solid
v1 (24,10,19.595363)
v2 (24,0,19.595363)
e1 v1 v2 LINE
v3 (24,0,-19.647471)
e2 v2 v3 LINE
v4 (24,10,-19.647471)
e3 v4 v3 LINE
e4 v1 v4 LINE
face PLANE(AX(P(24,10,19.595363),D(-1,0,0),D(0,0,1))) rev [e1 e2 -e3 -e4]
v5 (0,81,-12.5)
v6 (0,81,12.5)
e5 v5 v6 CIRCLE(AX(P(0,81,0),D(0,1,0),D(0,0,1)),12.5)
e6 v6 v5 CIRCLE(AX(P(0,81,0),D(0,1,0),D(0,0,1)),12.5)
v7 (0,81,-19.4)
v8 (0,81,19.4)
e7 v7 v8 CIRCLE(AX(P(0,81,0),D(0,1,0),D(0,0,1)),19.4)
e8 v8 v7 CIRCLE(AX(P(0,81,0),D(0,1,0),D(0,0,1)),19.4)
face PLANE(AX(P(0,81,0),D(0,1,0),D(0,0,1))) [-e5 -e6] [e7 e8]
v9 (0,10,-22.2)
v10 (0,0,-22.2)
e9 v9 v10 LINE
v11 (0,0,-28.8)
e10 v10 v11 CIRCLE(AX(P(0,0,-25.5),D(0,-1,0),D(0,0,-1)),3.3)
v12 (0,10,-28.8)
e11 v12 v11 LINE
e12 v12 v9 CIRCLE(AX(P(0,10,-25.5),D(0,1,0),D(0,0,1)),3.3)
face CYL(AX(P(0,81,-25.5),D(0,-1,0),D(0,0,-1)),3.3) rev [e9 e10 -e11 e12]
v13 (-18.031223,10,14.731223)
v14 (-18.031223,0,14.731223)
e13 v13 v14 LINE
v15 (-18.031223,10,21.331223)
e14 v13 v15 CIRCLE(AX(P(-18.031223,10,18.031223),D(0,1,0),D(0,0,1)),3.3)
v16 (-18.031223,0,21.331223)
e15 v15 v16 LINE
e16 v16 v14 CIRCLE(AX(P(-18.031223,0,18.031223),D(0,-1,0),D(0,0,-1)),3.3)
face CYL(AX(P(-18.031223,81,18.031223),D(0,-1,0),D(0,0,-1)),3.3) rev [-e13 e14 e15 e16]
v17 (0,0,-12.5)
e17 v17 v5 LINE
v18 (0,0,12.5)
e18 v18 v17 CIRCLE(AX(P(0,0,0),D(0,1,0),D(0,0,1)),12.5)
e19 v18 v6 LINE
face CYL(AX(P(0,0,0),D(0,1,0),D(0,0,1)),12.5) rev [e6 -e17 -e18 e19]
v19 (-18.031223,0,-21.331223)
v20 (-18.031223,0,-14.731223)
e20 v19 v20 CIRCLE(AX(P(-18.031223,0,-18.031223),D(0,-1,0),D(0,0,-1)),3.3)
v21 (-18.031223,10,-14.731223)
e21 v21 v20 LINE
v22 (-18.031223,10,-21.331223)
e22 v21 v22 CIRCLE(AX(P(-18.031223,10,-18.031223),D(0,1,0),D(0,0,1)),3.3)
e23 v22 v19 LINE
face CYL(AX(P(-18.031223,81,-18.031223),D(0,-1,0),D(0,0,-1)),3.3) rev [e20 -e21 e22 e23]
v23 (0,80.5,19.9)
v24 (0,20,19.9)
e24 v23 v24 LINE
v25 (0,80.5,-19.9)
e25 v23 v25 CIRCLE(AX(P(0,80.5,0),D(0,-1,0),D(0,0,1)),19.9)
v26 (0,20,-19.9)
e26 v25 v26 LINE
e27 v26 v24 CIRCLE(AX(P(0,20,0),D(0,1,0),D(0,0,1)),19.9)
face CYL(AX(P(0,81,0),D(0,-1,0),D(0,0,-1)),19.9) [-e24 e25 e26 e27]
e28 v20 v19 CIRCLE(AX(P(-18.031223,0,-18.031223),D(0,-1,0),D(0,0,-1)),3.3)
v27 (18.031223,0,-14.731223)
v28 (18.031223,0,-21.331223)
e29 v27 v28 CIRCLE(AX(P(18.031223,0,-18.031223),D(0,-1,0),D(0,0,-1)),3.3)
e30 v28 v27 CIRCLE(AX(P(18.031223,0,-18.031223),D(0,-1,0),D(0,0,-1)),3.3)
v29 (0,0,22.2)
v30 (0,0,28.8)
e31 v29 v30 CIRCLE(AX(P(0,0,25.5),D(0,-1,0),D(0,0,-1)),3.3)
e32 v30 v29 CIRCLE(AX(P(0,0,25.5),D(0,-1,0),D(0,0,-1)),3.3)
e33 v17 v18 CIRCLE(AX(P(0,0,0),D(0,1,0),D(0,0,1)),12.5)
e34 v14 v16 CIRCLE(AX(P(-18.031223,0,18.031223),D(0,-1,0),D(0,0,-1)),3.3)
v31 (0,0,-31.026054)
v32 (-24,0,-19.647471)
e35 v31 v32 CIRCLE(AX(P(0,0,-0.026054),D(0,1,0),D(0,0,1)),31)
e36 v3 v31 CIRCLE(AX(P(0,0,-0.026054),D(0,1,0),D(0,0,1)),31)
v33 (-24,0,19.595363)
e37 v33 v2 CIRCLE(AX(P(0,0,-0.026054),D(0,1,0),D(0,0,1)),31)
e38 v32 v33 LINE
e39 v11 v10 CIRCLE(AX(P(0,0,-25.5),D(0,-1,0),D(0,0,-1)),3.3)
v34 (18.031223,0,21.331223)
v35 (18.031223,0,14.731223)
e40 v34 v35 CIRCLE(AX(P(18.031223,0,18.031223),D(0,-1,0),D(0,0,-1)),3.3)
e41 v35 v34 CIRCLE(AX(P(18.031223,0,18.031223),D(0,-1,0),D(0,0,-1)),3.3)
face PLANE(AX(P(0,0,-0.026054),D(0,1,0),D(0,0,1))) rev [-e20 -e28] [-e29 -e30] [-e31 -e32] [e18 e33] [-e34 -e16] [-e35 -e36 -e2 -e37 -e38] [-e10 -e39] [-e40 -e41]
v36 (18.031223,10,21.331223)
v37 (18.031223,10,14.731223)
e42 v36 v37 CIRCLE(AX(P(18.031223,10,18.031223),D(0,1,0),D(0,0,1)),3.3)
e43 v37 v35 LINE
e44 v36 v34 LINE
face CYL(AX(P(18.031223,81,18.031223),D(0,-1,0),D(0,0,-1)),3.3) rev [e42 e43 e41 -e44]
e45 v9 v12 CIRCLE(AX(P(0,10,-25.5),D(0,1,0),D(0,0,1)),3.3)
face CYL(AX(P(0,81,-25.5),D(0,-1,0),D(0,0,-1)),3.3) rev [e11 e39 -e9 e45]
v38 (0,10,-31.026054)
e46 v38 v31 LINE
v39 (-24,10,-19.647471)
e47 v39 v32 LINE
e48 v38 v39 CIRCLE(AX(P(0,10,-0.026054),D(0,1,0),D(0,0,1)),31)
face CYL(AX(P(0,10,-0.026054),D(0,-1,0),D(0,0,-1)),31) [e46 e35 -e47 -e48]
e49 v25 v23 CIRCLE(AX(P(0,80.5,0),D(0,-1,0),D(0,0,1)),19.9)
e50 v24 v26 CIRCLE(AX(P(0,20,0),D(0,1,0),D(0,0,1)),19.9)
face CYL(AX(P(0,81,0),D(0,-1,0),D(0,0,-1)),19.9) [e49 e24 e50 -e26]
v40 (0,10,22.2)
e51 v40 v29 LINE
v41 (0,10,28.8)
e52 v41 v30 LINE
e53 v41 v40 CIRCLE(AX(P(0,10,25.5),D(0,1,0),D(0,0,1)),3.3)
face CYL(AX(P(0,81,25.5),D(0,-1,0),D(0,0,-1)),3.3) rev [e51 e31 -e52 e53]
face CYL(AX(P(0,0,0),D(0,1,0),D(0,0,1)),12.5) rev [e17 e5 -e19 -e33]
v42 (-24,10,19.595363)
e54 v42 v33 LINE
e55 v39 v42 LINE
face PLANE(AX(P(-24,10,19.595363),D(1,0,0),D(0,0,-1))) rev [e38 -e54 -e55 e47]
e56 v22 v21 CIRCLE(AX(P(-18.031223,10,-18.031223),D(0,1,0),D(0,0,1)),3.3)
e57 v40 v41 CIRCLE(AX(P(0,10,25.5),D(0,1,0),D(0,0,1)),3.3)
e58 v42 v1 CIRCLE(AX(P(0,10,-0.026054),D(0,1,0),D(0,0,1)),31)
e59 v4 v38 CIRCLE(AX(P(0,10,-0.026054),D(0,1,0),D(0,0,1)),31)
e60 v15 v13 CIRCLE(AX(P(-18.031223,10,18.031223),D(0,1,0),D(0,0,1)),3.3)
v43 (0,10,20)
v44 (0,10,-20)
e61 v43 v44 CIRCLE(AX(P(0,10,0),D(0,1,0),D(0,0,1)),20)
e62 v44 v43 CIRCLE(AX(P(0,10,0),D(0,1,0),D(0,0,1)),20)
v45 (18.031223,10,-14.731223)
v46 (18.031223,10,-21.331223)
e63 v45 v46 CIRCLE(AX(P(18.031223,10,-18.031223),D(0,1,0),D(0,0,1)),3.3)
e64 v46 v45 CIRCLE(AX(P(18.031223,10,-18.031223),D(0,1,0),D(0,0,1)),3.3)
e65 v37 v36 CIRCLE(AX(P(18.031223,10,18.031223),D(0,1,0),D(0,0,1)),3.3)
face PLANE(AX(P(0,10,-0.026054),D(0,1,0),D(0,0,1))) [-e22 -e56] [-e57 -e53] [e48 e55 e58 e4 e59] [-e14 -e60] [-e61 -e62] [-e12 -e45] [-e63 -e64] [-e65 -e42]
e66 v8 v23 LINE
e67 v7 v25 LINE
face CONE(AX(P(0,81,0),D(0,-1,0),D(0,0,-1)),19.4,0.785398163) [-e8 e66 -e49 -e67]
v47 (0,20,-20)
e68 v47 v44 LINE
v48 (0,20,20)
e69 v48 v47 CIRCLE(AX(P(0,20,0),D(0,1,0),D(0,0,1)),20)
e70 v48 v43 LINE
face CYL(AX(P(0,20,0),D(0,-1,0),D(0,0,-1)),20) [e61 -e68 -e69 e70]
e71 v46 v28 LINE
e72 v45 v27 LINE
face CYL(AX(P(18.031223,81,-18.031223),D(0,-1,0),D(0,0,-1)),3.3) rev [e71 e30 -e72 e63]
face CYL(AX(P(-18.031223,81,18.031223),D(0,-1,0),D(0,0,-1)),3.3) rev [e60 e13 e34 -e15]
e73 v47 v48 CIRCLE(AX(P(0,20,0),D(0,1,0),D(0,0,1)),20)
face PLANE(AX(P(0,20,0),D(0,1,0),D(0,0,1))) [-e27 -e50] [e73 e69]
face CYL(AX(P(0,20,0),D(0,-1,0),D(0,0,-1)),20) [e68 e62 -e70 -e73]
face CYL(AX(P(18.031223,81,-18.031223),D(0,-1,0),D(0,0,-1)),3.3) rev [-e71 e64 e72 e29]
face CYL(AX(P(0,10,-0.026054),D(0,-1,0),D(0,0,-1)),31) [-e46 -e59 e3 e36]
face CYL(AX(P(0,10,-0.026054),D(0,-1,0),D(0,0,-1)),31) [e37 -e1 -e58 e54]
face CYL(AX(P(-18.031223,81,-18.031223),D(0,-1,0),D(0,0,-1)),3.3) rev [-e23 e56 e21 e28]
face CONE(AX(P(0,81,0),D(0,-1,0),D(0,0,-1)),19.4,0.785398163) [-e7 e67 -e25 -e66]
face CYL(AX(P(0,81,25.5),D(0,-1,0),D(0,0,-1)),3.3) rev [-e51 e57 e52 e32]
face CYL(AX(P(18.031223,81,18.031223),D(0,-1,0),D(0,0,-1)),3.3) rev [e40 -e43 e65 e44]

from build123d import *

# Parameters (mm, degrees)
EXTRUDE_1_DEPTH     = 10
SKETCH_2_R          = 20
EXTRUDE_2_DEPTH     = 10
SKETCH_3_R          = 19.9
EXTRUDE_3_DEPTH     = 61
SKETCH_5_R          = 12.5
CUT_EXTRUDE_1_DEPTH = 90.997866916
SKETCH_6_R          = 3.3
CUT_EXTRUDE_2_DEPTH = 90.997866916
CHAMFER_1_SIZE      = 0.5


with BuildPart() as part:
    # 草图1 → 拉伸1 (new body)
    with BuildSketch(Plane(origin=(0, 0, 0), x_dir=(1, 0, 0), z_dir=(0, 1, 0))):
        with BuildLine():
            Line((24, -19.595362506), (24, 19.647471235))
            ThreePointArc((24, 19.647471235), (0, 31.026054364), (-24, 19.647471235))
            Line((-24, 19.647471235), (-24, -19.595362506))
            ThreePointArc((-24, -19.595362506), (0, -30.973945636), (24, -19.595362506))
        make_face()
    extrude(amount=EXTRUDE_1_DEPTH)

    # 草图2 → 拉伸2 (add)
    with BuildSketch(Plane(origin=(0, 10, 0), x_dir=(-1, 0, 0), z_dir=(0, 1, 0))):
        with Locations(Location((0, 0, 0), (0, 0, 90))):
            Circle(SKETCH_2_R)
    extrude(amount=EXTRUDE_2_DEPTH)

    # 草图3 → 拉伸3 (add)
    with BuildSketch(Plane(origin=(0, 20, 0), x_dir=(-1, 0, 0), z_dir=(0, 1, 0))):
        with Locations(Location((0, 0, 0), (0, 0, 270))):
            Circle(SKETCH_3_R)
    extrude(amount=EXTRUDE_3_DEPTH)

    # 草图5 → 切除-拉伸1 (cut, through all)
    with BuildSketch(Plane(origin=(0, 81, 0), x_dir=(-1, 0, 0), z_dir=(0, 1, 0))):
        with Locations(Location((0, 0, 0), (0, 0, 90))):
            Circle(SKETCH_5_R)
    extrude(amount=-CUT_EXTRUDE_1_DEPTH, mode=Mode.SUBTRACT)

    # 草图6 → 切除-拉伸2 (cut, through all)
    with BuildSketch(Plane.XZ):
        with Locations(Location((18.03122292, -18.03122292, 0), (0, 0, 270))):
            Circle(SKETCH_6_R)
        with Locations(Location((0, -25.5, 0), (0, 0, 270))):
            Circle(SKETCH_6_R)
        with Locations(Location((-18.03122292, -18.03122292, 0), (0, 0, 270))):
            Circle(SKETCH_6_R)
        with Locations(Location((-18.03122292, 18.03122292, 0), (0, 0, 270))):
            Circle(SKETCH_6_R)
        with Locations(Location((0, 25.5, 0), (0, 0, 270))):
            Circle(SKETCH_6_R)
        with Locations(Location((18.03122292, 18.03122292, 0), (0, 0, 270))):
            Circle(SKETCH_6_R)
    extrude(amount=-CUT_EXTRUDE_2_DEPTH, mode=Mode.SUBTRACT)

    # 倒角1
    chamfer_1_edges = [part.edges().sort_by_distance(p)[0] for p in [
        (0, 81, 19.9),
    ]]
    chamfer(chamfer_1_edges, length=CHAMFER_1_SIZE)


solid = part.part
